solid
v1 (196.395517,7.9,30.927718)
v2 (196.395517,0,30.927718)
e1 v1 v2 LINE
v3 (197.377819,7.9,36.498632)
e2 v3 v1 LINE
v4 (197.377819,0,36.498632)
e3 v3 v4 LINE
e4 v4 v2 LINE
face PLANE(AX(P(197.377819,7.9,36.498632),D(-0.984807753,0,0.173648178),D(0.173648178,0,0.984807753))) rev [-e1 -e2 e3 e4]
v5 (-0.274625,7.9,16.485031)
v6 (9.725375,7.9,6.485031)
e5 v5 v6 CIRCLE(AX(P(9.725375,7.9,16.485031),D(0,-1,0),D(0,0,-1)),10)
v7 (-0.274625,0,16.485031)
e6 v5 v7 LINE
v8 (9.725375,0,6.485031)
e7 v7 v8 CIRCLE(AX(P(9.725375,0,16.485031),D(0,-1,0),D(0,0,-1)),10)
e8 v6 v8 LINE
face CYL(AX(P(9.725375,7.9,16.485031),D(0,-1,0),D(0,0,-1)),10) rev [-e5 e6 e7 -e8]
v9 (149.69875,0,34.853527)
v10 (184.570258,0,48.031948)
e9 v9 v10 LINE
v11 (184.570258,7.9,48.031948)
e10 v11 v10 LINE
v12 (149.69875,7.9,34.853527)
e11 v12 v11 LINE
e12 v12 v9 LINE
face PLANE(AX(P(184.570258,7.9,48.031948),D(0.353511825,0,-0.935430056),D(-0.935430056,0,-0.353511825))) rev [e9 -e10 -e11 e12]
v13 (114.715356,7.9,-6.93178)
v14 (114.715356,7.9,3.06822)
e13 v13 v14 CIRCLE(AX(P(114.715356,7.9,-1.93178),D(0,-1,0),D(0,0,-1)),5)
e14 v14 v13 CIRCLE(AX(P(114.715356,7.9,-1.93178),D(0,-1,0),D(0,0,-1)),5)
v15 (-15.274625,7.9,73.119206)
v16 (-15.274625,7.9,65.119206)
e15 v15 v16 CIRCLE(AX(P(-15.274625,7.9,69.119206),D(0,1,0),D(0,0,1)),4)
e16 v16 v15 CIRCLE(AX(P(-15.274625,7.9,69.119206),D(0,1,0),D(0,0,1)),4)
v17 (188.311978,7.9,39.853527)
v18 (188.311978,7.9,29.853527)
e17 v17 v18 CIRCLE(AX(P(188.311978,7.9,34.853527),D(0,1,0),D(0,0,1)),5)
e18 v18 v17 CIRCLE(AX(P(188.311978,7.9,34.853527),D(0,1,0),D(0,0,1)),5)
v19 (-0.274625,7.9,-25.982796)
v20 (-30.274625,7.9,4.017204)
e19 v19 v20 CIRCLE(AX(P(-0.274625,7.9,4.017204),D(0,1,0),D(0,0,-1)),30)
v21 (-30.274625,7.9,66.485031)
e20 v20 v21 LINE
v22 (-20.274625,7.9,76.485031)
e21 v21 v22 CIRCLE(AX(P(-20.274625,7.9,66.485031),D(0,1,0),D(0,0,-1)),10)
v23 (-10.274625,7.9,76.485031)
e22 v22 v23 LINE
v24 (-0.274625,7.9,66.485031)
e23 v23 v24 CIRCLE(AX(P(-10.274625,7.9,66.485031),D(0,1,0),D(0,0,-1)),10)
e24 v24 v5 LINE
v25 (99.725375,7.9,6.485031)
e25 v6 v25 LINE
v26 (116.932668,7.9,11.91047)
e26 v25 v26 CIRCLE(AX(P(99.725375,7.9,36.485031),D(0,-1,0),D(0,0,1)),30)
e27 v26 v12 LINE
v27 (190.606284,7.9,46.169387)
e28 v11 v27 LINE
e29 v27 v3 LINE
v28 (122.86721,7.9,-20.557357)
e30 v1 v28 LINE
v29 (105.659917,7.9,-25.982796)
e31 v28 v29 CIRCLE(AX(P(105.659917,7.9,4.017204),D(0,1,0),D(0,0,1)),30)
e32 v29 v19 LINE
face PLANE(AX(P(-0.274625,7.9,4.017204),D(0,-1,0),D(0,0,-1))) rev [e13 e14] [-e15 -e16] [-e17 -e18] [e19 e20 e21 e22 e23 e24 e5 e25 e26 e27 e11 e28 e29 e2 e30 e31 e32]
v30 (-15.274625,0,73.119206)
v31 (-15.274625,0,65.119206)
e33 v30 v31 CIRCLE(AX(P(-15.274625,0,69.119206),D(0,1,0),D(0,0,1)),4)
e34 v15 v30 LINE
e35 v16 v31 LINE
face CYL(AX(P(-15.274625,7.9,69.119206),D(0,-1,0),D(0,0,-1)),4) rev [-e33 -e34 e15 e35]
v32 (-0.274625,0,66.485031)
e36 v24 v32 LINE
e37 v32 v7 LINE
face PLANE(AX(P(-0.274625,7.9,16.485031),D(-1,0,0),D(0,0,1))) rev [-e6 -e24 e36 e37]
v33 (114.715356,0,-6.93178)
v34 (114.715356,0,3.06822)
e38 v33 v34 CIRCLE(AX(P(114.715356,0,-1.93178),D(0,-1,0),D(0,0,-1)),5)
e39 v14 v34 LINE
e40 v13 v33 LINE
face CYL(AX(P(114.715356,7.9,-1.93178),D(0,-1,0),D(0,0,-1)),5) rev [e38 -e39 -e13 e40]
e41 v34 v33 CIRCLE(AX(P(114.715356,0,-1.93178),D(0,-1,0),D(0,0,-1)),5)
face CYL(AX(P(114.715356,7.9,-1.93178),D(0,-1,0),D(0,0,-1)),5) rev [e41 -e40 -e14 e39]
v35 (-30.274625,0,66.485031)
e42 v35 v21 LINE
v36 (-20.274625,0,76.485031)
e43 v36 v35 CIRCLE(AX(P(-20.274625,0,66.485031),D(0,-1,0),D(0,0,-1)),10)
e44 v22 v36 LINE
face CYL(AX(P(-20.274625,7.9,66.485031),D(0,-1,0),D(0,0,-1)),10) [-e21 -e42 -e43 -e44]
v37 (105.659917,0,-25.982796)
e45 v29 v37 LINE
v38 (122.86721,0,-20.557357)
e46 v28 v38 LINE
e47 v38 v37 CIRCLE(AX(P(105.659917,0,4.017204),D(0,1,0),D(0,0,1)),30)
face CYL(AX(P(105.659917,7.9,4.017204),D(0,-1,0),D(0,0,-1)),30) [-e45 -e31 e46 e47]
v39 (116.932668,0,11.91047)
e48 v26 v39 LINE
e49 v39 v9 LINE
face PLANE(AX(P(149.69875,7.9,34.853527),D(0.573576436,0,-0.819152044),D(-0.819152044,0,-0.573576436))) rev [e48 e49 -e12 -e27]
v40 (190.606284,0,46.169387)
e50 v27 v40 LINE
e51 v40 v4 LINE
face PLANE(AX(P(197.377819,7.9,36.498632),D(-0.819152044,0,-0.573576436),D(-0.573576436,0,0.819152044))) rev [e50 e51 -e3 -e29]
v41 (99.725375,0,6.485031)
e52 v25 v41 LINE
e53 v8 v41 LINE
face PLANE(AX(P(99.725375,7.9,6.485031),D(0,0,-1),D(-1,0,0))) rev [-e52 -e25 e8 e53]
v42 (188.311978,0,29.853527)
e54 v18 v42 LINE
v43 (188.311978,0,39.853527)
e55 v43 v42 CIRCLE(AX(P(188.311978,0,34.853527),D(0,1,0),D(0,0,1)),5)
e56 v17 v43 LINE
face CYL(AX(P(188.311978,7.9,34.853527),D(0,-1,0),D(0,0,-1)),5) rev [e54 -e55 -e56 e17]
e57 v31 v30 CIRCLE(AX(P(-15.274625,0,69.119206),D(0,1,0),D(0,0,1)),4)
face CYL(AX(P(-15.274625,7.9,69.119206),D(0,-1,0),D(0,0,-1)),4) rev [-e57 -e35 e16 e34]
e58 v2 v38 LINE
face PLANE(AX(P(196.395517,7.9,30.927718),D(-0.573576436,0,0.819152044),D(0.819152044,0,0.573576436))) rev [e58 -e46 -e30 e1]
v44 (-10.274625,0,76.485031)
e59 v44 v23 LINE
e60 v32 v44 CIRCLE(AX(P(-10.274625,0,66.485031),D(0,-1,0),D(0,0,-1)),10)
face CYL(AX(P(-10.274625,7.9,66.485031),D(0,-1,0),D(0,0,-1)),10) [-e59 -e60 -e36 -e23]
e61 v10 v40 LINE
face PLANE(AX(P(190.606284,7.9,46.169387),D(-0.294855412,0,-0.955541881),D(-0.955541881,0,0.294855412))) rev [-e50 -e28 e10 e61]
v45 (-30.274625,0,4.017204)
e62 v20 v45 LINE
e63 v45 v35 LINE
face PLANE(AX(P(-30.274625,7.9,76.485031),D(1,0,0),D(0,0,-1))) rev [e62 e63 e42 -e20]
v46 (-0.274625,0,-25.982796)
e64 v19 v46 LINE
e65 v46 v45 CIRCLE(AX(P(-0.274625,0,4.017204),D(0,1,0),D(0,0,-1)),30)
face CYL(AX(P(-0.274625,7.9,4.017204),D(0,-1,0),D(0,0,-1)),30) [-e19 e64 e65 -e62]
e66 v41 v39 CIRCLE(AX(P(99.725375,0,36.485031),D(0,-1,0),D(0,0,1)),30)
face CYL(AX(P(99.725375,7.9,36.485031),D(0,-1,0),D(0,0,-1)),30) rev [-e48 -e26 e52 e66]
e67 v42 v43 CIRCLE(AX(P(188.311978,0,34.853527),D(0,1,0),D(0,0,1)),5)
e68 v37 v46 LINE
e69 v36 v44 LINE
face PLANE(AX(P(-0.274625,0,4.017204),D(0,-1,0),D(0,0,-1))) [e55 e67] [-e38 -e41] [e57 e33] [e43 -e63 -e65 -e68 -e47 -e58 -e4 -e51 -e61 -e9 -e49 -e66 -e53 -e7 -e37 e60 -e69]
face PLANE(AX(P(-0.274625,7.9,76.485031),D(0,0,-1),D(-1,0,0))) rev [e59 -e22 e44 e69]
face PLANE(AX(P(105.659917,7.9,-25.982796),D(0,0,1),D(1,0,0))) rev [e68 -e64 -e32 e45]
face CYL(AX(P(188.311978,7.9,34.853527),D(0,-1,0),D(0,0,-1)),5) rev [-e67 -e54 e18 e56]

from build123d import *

# Parameters (mm, degrees)
SKETCH1_R          = 5
SKETCH1_R_2        = 4
BOSS_EXTRU_1_DEPTH = 7.9
SKETCH2_R          = 5
CUT_EXTRUDE1_DEPTH = 212.826281623
FILLET1_R          = 10


with BuildPart() as part:
    # Sketch1 → Boss.-Extru.1 (new body)
    with BuildSketch(Plane(origin=(0, 0, 0), x_dir=(1, 0, 0), z_dir=(0, 1, 0))):
        with BuildLine():
            Line((149.698750242, -34.853527415), (116.932668471, -11.910469961))
            ThreePointArc((116.932668471, -11.910469961), (108.746549365, -7.873522768), (99.72537538, -6.48503129))
            Line((99.72537538, -6.48503129), (9.72537538, -6.48503129))
            ThreePointArc((9.72537538, -6.48503129), (2.654307568, -9.413963478), (-0.27462462, -16.48503129))
            Line((-0.27462462, -16.48503129), (-0.27462462, -76.48503129))
            Line((-0.27462462, -76.48503129), (-30.27462462, -76.48503129))
            Line((-30.27462462, -76.48503129), (-30.27462462, -4.017204085))
            ThreePointArc((-30.27462462, -4.017204085), (-21.487828056, 17.195999351), (-0.27462462, 25.982795915))
            Line((-0.27462462, 25.982795915), (105.659916542, 25.982795915))
            ThreePointArc((105.659916542, 25.982795915), (114.681090527, 24.594304438), (122.867209633, 20.557357244))
            Line((122.867209633, 20.557357244), (196.395516927, -30.927717795))
            Line((196.395516927, -30.927717795), (197.377819359, -36.498631718))
            Line((197.377819359, -36.498631718), (190.606283823, -46.169386696))
            Line((190.606283823, -46.169386696), (184.570257854, -48.031947572))
            Line((184.570257854, -48.031947572), (149.698750242, -34.853527415))
        make_face()
        with Locations(Location((188.311978078, -34.853527415, 0), (0, 0, 270))):
            Circle(SKETCH1_R, mode=Mode.SUBTRACT)
        with Locations(Location((-15.27462462, -69.11920583, 0), (0, 0, 270))):
            Circle(SKETCH1_R_2, mode=Mode.SUBTRACT)
    extrude(amount=BOSS_EXTRU_1_DEPTH)

    # Sketch2 → Cut-Extrude1 (cut, through all)
    with BuildSketch(Plane.XZ):
        with Locations(Location((114.715355874, -1.93178017, 0), (0, 0, 270))):
            Circle(SKETCH2_R)
    extrude(amount=-CUT_EXTRUDE1_DEPTH, mode=Mode.SUBTRACT)

    # Fillet1
    fillet1_edges = [part.edges().sort_by_distance(p)[0] for p in [
        (-30.27462462, 3.95, 76.48503129),
        (-0.27462462, 3.95, 76.48503129),
    ]]
    fillet(fillet1_edges, radius=FILLET1_R)


solid = part.part
